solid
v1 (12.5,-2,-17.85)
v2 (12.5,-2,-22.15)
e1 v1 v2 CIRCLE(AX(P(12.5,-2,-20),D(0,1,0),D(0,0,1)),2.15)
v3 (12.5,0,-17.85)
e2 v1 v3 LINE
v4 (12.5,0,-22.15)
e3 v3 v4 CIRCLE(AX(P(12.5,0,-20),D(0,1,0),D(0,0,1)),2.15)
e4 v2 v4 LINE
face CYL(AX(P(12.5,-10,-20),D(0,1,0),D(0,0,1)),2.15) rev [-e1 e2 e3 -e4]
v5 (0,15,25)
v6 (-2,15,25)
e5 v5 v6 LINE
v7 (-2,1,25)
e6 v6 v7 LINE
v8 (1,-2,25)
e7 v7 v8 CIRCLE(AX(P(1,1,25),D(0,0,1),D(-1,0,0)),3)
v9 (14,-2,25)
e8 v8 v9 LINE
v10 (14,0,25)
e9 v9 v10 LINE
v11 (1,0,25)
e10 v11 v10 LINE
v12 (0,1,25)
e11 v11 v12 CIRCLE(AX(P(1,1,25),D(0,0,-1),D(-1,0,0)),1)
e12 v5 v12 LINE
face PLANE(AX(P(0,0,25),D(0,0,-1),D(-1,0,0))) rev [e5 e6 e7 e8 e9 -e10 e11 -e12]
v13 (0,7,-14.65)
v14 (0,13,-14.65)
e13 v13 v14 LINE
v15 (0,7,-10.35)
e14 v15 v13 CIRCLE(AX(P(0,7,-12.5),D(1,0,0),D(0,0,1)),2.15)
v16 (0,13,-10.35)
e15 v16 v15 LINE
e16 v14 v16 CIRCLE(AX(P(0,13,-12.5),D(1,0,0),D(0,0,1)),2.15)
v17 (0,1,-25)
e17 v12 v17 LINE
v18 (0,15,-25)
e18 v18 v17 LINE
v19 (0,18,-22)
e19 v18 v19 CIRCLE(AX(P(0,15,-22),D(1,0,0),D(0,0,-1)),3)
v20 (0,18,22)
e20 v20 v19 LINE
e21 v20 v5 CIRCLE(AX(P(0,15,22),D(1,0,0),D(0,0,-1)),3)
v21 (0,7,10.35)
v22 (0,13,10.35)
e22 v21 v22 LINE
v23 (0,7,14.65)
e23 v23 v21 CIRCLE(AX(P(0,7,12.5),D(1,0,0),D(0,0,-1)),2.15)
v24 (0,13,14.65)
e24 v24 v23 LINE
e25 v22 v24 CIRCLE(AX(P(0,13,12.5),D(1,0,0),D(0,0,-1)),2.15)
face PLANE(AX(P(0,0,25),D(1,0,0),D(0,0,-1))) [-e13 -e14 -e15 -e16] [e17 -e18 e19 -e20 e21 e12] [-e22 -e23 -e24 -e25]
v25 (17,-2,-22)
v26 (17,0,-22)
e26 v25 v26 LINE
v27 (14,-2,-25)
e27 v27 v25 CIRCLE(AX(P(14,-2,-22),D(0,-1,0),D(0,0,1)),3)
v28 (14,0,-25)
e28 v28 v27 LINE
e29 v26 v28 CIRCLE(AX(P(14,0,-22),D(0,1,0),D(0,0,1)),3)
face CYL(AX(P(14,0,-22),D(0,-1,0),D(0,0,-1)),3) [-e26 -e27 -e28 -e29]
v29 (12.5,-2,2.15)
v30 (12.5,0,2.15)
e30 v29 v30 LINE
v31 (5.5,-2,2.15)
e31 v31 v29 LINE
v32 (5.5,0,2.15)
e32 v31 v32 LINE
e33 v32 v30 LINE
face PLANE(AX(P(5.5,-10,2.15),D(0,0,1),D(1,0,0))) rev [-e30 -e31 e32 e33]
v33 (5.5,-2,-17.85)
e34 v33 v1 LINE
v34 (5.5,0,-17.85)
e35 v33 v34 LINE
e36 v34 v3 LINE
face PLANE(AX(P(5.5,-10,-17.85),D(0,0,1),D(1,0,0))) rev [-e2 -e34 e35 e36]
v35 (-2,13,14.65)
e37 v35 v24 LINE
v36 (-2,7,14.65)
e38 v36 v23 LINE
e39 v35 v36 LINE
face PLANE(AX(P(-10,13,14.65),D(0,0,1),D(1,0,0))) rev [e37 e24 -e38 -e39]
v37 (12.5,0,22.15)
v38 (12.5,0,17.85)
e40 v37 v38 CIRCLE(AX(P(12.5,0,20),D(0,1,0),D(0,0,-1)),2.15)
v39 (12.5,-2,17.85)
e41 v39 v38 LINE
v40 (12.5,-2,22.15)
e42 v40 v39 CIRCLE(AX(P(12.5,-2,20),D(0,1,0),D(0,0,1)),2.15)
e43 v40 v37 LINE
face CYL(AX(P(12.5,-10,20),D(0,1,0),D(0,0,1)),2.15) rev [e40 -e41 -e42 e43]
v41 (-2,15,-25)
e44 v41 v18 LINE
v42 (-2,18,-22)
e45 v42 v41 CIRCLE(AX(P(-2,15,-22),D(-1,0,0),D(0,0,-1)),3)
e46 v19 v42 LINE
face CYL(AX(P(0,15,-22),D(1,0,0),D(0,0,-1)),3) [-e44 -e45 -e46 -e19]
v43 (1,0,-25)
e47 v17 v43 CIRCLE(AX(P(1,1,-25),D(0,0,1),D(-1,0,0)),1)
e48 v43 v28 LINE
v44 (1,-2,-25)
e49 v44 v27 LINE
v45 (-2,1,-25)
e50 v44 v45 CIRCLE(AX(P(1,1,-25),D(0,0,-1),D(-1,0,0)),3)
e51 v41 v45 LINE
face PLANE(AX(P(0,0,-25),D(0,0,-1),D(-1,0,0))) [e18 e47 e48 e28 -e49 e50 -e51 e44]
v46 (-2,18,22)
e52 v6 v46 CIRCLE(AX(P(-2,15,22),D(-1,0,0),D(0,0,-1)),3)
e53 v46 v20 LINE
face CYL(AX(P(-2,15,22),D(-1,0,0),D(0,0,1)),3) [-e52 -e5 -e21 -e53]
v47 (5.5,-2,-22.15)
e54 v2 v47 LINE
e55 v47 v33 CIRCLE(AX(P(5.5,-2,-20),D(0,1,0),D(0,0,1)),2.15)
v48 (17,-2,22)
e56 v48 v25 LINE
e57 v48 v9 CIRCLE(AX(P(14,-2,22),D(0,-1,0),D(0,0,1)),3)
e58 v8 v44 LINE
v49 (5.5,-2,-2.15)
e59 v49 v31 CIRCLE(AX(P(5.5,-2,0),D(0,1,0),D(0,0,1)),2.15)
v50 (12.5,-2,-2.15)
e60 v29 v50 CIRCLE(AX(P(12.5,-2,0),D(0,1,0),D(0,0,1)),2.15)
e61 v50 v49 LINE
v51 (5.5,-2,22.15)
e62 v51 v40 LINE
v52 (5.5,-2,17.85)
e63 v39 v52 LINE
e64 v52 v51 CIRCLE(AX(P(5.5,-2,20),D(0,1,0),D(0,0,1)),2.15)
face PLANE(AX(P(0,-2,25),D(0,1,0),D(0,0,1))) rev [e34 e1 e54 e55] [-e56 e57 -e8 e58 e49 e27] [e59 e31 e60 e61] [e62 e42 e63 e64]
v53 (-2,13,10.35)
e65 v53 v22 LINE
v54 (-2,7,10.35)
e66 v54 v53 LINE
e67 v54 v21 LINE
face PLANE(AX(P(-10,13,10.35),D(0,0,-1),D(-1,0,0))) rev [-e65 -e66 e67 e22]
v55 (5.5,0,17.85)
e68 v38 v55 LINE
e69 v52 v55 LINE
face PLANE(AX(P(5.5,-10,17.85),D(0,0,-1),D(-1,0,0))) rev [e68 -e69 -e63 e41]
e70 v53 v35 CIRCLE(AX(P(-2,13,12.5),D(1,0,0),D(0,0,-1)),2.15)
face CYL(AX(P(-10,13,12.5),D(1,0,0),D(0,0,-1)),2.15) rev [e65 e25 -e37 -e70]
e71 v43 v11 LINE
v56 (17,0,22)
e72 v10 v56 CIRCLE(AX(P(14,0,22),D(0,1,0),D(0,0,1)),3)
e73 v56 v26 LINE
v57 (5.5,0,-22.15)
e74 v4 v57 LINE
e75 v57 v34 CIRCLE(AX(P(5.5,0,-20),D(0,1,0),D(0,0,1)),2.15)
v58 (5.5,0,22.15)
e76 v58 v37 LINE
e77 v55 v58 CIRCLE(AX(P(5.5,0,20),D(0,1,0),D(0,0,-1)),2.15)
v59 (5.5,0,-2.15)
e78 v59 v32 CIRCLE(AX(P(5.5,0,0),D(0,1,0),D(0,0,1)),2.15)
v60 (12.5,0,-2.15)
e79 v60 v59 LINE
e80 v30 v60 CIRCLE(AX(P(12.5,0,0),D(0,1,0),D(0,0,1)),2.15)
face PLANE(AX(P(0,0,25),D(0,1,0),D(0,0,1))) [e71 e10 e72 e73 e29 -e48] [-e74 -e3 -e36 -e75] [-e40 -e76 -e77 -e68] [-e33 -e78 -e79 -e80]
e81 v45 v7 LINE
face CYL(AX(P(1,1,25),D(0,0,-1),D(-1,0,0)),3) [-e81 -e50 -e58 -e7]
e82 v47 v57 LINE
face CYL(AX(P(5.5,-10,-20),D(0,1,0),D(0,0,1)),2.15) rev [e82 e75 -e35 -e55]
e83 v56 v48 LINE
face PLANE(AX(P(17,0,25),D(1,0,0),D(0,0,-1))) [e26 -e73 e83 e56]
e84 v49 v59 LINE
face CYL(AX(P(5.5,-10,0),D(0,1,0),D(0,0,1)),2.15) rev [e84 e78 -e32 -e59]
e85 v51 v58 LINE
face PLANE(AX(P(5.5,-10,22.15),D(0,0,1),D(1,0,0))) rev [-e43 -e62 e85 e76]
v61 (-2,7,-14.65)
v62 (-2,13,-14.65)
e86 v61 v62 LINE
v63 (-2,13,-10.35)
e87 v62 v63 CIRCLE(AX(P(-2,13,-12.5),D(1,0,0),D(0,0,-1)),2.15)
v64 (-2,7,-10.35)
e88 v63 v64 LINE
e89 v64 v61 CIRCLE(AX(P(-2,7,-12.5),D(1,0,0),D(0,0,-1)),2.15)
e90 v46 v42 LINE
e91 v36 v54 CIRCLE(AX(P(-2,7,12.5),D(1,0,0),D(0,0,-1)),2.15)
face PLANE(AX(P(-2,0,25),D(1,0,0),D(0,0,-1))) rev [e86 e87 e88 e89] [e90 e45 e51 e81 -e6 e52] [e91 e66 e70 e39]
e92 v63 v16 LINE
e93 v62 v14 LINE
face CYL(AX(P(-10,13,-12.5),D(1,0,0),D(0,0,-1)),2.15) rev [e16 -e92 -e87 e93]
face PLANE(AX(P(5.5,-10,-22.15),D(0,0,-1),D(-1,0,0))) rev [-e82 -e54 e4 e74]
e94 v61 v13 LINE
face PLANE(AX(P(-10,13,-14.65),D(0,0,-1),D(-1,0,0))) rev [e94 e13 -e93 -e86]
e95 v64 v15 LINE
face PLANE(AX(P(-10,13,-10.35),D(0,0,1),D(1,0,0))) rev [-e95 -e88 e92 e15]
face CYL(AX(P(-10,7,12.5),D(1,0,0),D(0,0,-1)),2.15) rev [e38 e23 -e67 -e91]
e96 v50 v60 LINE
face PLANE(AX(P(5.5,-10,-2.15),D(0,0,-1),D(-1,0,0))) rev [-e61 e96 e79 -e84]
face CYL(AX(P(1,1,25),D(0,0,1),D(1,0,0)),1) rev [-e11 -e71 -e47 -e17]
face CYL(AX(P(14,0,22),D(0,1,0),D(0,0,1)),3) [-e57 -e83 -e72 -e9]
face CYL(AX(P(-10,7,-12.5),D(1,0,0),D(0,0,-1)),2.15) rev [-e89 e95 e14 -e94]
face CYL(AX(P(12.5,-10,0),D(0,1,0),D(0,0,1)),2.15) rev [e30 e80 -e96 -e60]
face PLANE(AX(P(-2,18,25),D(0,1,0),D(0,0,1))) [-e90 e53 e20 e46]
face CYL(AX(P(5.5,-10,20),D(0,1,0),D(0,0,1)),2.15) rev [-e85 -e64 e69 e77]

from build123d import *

# Parameters (mm, degrees)
EXTRUDE_1_DEPTH     = 25
CUT_EXTRUDE_1_DEPTH = 10
CUT_EXTRUDE_2_DEPTH = 10
FILLET_1_R          = 3
FILLET_2_R          = 1
FILLET_3_R          = 3


with BuildPart() as part:
    # 草图9 → 拉伸-薄壁1 (new, symmetric)
    with BuildSketch(Plane.XY):
        Polygon((17, 0), (0, 0), (0, 18), (-2, 18), (-2, -2), (17, -2), align=None)
    extrude(amount=EXTRUDE_1_DEPTH, both=True)

    # 草图10 → 切除-拉伸1 (cut)
    with BuildSketch(Plane(origin=(0, 0, 0), x_dir=(1, 0, 0), z_dir=(0, 1, 0))):
        with BuildLine():
            Line((5.5, 22.15), (12.5, 22.15))
            ThreePointArc((12.5, 22.15), (14.65, 20), (12.5, 17.85))
            Line((12.5, 17.85), (5.5, 17.85))
            ThreePointArc((5.5, 17.85), (3.35, 20), (5.5, 22.15))
        make_face()
        with BuildLine():
            Line((5.5, -22.15), (12.5, -22.15))
            ThreePointArc((12.5, -22.15), (14.65, -20), (12.5, -17.85))
            Line((12.5, -17.85), (5.5, -17.85))
            ThreePointArc((5.5, -17.85), (3.35, -20), (5.5, -22.15))
        make_face()
        with BuildLine():
            Line((5.5, 2.15), (12.5, 2.15))
            ThreePointArc((12.5, 2.15), (14.65, 0), (12.5, -2.15))
            Line((12.5, -2.15), (5.5, -2.15))
            ThreePointArc((5.5, -2.15), (3.35, 0), (5.5, 2.15))
        make_face()
    extrude(amount=-CUT_EXTRUDE_1_DEPTH, mode=Mode.SUBTRACT)

    # 草图11 → 切除-拉伸2 (cut)
    with BuildSketch(Plane(origin=(0, 0, 0), x_dir=(0, 0, -1), z_dir=(1, 0, 0))):
        with BuildLine():
            Line((-10.35, 13), (-10.35, 7))
            ThreePointArc((-10.35, 7), (-12.5, 4.85), (-14.65, 7))
            Line((-14.65, 7), (-14.65, 13))
            ThreePointArc((-14.65, 13), (-12.5, 15.15), (-10.35, 13))
        make_face()
        with BuildLine():
            Line((10.35, 13), (10.35, 7))
            ThreePointArc((10.35, 7), (12.5, 4.85), (14.65, 7))
            Line((14.65, 7), (14.65, 13))
            ThreePointArc((14.65, 13), (12.5, 15.15), (10.35, 13))
        make_face()
    extrude(amount=-CUT_EXTRUDE_2_DEPTH, mode=Mode.SUBTRACT)

    # 圆角1
    fillet_1_edges = [part.edges().sort_by_distance(p)[0] for p in [
        (-1, 18, 25),
        (-1, 18, -25),
        (17, -1, -25),
        (17, -1, 25),
    ]]
    fillet(fillet_1_edges, radius=FILLET_1_R)

    # 圆角2
    fillet_2_edges = [part.edges().sort_by_distance(p)[0] for p in [
        (0, 0, 0),
    ]]
    fillet(fillet_2_edges, radius=FILLET_2_R)

    # 圆角3
    fillet_3_edges = [part.edges().sort_by_distance(p)[0] for p in [
        (-2, -2, 0),
    ]]
    fillet(fillet_3_edges, radius=FILLET_3_R)


solid = part.part
